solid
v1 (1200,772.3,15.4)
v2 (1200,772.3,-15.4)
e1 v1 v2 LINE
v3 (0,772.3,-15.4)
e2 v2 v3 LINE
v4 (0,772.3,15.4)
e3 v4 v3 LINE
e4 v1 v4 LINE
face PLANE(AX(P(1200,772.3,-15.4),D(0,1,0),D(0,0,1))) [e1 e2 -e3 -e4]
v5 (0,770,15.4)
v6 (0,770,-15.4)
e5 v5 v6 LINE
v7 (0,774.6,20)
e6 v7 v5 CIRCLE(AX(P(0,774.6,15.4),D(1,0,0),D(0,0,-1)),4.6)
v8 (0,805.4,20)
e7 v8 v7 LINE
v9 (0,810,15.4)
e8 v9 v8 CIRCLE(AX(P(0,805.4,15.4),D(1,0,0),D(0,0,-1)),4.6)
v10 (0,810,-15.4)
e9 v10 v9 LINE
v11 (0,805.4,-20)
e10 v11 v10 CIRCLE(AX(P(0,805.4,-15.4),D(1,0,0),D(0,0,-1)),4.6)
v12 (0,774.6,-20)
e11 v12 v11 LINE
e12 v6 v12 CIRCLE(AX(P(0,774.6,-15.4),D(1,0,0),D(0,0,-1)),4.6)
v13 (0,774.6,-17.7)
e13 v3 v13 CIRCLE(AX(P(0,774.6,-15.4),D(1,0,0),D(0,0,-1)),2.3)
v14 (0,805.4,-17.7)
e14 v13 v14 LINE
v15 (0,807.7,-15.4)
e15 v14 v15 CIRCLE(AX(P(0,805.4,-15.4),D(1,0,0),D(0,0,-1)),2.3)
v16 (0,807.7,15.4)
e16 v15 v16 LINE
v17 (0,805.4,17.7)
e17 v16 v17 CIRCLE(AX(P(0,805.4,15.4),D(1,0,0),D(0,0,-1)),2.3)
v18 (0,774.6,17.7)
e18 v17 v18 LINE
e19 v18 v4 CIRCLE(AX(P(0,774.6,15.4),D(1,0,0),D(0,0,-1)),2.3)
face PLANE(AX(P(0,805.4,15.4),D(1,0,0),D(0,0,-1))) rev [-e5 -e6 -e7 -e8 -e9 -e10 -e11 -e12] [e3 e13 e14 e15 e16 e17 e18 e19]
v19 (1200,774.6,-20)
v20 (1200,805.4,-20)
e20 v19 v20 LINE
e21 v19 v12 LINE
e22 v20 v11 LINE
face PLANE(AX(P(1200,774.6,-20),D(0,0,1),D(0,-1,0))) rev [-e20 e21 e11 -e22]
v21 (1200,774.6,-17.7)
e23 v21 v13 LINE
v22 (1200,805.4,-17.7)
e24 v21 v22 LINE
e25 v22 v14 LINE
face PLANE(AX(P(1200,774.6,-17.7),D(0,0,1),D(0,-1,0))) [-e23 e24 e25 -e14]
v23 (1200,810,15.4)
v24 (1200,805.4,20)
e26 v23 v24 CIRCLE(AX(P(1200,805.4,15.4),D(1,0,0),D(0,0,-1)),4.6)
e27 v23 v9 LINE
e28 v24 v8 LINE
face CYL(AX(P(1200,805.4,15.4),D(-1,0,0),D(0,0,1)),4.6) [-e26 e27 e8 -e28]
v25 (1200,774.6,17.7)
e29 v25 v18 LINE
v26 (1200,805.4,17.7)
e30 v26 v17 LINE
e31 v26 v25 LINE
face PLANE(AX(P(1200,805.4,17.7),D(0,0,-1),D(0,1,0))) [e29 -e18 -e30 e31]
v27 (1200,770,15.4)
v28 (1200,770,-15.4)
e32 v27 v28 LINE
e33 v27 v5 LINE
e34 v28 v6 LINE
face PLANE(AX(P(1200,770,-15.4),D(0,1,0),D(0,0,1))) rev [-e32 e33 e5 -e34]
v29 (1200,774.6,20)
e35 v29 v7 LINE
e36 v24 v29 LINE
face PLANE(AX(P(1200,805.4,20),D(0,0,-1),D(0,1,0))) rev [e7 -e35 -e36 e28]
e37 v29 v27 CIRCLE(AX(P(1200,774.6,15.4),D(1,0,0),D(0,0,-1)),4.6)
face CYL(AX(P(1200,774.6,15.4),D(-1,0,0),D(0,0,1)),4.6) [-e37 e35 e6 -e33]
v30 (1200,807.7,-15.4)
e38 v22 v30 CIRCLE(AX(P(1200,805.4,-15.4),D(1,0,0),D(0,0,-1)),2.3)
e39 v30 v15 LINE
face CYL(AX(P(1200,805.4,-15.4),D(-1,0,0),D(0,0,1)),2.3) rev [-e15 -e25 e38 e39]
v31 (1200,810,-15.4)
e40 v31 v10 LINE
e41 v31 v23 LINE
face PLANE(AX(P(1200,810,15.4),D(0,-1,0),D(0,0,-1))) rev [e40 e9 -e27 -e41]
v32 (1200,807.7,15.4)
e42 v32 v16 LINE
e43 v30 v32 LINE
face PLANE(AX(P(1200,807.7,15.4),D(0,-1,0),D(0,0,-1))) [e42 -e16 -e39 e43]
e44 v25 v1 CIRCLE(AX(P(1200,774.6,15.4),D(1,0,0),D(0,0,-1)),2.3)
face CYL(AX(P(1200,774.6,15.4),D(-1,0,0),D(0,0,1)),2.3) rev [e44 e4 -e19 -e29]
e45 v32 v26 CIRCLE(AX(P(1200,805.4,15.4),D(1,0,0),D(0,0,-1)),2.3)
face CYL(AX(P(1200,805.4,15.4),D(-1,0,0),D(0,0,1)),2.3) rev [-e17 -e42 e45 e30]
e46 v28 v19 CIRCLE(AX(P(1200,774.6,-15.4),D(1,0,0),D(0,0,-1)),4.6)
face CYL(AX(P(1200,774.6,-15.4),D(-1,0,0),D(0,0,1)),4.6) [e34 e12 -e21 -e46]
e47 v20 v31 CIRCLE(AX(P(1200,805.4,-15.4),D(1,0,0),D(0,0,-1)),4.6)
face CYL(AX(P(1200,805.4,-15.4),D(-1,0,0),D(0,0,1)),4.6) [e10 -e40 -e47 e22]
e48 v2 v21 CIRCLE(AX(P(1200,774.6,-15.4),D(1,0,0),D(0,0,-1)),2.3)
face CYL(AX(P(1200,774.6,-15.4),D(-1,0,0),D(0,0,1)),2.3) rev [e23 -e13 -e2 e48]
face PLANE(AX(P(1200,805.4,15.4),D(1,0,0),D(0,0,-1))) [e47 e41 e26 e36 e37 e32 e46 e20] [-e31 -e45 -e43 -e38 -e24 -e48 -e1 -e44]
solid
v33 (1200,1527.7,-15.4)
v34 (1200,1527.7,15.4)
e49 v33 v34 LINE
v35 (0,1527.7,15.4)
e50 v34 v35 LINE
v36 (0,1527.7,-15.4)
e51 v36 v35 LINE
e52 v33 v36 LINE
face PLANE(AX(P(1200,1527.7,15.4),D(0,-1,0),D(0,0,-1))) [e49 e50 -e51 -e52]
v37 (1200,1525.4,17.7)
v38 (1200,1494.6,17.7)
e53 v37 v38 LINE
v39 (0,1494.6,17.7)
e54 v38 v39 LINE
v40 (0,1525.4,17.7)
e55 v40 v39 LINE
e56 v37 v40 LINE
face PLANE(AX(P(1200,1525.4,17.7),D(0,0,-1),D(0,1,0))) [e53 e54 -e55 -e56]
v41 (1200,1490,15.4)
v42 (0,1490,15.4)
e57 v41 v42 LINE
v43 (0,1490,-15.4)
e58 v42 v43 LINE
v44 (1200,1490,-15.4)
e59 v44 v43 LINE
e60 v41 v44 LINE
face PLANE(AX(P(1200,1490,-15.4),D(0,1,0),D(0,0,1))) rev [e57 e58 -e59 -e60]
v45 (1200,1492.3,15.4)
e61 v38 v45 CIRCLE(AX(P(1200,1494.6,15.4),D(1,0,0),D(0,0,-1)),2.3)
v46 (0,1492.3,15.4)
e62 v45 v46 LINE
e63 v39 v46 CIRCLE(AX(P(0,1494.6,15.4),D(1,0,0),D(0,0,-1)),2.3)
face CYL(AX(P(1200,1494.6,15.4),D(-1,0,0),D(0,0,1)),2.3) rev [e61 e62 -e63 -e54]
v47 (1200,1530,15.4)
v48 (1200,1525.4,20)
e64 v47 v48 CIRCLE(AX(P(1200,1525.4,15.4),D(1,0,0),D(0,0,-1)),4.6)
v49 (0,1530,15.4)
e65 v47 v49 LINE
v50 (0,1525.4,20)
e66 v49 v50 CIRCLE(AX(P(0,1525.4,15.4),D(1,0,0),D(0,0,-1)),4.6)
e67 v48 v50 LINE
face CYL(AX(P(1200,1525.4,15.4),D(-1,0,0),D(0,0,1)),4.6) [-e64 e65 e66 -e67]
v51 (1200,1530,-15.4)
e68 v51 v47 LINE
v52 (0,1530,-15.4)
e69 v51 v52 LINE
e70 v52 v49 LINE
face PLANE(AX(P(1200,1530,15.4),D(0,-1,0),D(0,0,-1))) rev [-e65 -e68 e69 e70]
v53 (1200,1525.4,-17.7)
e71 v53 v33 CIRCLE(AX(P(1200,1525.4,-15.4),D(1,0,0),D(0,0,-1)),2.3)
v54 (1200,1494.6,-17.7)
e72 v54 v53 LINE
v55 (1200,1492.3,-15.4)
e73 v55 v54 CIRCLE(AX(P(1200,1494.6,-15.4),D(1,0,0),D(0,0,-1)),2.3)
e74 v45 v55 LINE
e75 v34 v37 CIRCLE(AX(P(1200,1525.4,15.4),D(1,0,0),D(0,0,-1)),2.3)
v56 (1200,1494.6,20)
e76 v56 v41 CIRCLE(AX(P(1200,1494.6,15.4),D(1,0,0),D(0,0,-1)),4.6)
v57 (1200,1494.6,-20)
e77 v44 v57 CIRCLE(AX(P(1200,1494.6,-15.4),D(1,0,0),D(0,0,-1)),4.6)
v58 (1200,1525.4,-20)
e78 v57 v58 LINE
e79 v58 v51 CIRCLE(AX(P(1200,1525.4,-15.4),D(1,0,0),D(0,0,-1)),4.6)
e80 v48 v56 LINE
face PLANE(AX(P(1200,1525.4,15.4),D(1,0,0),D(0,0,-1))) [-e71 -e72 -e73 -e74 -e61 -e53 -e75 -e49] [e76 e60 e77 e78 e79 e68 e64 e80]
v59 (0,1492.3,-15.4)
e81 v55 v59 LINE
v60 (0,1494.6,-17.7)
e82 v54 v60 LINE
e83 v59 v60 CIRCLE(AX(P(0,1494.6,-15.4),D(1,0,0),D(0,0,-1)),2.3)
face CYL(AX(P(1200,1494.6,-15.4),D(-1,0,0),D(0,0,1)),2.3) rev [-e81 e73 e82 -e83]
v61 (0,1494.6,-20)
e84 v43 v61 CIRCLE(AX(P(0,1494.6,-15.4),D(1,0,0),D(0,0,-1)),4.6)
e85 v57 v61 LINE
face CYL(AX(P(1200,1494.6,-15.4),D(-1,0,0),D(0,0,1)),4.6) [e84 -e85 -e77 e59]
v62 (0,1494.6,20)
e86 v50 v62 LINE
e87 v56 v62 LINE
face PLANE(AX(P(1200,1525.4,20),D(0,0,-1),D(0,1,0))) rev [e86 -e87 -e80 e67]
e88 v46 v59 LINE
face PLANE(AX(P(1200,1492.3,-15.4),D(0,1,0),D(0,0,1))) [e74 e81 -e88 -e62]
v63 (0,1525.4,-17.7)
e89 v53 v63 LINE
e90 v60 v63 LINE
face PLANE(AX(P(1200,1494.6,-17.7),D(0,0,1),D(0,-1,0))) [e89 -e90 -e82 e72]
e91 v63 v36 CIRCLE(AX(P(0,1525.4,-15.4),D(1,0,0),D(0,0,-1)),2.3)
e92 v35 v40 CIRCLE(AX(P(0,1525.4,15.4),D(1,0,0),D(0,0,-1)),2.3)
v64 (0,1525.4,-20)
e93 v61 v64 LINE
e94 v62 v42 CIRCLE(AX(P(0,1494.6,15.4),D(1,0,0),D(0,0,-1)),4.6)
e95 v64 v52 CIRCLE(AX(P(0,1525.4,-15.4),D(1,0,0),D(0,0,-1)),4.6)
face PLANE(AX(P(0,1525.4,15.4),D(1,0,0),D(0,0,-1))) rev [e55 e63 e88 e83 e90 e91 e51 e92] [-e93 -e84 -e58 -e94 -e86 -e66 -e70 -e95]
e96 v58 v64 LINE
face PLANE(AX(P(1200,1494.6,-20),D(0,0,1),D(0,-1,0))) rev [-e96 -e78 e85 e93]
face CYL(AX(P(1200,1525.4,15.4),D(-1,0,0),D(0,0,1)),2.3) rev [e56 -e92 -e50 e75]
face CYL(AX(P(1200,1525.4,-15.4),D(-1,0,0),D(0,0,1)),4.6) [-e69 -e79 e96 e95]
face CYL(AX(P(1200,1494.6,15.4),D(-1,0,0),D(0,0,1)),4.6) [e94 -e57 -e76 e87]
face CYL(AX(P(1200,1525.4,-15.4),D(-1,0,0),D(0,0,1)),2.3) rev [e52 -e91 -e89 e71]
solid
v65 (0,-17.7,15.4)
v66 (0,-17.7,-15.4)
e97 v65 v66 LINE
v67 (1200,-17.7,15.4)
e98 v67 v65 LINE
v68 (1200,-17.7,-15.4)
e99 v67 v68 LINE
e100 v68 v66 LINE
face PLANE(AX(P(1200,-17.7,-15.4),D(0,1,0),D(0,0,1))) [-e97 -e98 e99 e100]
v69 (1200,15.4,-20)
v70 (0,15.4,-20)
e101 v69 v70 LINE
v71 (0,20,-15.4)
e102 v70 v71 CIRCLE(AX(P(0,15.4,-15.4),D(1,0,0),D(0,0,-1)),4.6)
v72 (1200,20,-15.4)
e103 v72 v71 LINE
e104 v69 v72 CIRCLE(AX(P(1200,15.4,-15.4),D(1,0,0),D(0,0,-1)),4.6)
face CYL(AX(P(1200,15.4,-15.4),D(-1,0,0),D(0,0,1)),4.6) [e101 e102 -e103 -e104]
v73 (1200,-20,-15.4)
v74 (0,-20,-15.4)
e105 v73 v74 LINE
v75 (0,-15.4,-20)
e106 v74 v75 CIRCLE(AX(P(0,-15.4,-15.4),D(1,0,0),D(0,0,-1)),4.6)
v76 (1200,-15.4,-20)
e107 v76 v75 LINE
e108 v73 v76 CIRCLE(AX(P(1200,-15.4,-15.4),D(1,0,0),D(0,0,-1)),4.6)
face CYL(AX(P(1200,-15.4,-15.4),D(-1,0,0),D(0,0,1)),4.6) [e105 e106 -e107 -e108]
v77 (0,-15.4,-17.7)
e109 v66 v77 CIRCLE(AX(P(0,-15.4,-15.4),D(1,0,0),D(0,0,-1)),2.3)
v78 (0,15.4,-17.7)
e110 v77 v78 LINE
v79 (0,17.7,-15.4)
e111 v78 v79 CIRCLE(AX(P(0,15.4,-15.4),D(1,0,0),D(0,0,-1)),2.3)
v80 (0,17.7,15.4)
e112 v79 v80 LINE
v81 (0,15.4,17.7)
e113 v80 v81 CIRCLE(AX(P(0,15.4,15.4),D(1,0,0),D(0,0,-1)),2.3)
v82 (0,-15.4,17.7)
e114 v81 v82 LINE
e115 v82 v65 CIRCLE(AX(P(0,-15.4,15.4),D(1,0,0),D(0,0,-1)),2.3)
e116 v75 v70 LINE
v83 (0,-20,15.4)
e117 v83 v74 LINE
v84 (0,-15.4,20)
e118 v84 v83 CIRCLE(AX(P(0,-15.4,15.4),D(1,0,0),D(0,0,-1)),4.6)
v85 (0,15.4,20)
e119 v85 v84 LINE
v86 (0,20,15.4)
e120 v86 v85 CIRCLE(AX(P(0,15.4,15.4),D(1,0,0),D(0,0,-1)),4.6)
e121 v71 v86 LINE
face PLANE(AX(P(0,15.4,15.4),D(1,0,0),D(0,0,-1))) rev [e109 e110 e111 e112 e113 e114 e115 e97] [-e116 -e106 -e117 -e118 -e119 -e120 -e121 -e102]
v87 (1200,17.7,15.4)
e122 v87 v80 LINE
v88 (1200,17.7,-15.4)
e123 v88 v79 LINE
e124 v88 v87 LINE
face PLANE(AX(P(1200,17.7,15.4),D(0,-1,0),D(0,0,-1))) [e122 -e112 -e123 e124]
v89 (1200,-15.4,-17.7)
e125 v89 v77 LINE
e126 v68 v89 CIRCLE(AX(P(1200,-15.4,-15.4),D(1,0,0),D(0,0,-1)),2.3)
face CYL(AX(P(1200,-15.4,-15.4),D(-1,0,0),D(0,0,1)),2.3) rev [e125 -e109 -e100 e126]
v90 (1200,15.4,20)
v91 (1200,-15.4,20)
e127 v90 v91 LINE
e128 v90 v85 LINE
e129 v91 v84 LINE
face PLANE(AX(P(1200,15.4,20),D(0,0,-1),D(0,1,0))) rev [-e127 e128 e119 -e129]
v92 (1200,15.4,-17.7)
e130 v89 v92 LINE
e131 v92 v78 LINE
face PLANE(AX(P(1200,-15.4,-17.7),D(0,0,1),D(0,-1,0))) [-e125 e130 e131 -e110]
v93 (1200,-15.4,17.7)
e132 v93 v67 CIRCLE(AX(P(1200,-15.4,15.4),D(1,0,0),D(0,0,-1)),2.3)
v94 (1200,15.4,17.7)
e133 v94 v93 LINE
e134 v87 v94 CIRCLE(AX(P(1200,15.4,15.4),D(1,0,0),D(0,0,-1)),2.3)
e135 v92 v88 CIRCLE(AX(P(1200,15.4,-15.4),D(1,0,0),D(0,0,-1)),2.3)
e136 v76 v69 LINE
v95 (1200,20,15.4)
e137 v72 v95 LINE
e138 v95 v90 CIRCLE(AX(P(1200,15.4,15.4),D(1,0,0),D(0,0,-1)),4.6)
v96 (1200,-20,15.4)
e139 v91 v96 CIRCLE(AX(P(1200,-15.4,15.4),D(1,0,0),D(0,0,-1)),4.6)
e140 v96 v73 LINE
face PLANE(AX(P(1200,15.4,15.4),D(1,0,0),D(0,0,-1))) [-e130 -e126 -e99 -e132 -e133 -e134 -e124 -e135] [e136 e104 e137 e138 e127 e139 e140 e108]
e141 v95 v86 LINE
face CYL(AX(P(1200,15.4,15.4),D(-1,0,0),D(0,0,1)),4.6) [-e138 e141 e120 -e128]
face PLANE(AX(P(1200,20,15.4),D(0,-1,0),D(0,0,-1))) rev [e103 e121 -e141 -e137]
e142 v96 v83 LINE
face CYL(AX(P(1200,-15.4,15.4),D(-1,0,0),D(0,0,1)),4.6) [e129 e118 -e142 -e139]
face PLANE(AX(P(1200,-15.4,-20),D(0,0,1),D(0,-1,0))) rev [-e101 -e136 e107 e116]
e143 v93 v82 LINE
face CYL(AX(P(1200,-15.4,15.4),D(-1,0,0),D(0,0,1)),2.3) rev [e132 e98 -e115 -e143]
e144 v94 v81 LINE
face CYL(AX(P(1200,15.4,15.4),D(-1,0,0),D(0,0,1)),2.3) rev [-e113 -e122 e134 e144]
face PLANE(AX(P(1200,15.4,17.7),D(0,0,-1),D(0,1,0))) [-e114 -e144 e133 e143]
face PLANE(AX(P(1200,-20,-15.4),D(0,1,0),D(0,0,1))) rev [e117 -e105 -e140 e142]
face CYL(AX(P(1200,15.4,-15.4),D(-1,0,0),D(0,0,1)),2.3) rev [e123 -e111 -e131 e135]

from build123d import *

# Parameters (mm, degrees)
SQUARE_TUBE_40_X_40_X_2_3_1_DEPTH   = 1200
SQUARE_TUBE_40_X_40_X_2_3_1_2_DEPTH = 1200
SQUARE_TUBE_40_X_40_X_2_3_1_3_DEPTH = 1200


with BuildPart() as part:
    # Sketch11 → Square Tube 40 X 40 X 2.3(1) (new body)
    with BuildSketch(Plane.YZ):
        with BuildLine():
            Line((-15.4, -20), (15.4, -20))
            ThreePointArc((15.4, -20), (18.652691193, -18.652691193), (20, -15.4))
            Line((20, -15.4), (20, 15.4))
            ThreePointArc((20, 15.4), (18.652691193, 18.652691193), (15.4, 20))
            Line((15.4, 20), (-15.4, 20))
            ThreePointArc((-15.4, 20), (-18.652691193, 18.652691193), (-20, 15.4))
            Line((-20, 15.4), (-20, -15.4))
            ThreePointArc((-20, -15.4), (-18.652691193, -18.652691193), (-15.4, -20))
        make_face()
        with BuildLine():
            Line((-15.4, -17.7), (15.4, -17.7))
            ThreePointArc((15.4, -17.7), (17.026345597, -17.026345597), (17.7, -15.4))
            Line((17.7, -15.4), (17.7, 15.4))
            ThreePointArc((17.7, 15.4), (17.026345597, 17.026345597), (15.4, 17.7))
            Line((15.4, 17.7), (-15.4, 17.7))
            ThreePointArc((-15.4, 17.7), (-17.026345597, 17.026345597), (-17.7, 15.4))
            Line((-17.7, 15.4), (-17.7, -15.4))
            ThreePointArc((-17.7, -15.4), (-17.026345597, -17.026345597), (-15.4, -17.7))
        make_face(mode=Mode.SUBTRACT)
    extrude(amount=SQUARE_TUBE_40_X_40_X_2_3_1_DEPTH)


with BuildPart() as body_2:
    # Sketch11 on segment 2 (carried to segment 2) → Square Tube 40 X 40 X 2.3_1 2 (new body)
    with BuildSketch(Plane(origin=(0, 1510, 0), x_dir=(0, 1, 0), z_dir=(1, 0, 0))):
        with BuildLine():
            Line((-15.4, -20), (15.4, -20))
            ThreePointArc((15.4, -20), (18.652691193, -18.652691193), (20, -15.4))
            Line((20, -15.4), (20, 15.4))
            ThreePointArc((20, 15.4), (18.652691193, 18.652691193), (15.4, 20))
            Line((15.4, 20), (-15.4, 20))
            ThreePointArc((-15.4, 20), (-18.652691193, 18.652691193), (-20, 15.4))
            Line((-20, 15.4), (-20, -15.4))
            ThreePointArc((-20, -15.4), (-18.652691193, -18.652691193), (-15.4, -20))
        make_face()
        with BuildLine():
            Line((-15.4, -17.7), (15.4, -17.7))
            ThreePointArc((15.4, -17.7), (17.026345597, -17.026345597), (17.7, -15.4))
            Line((17.7, -15.4), (17.7, 15.4))
            ThreePointArc((17.7, 15.4), (17.026345597, 17.026345597), (15.4, 17.7))
            Line((15.4, 17.7), (-15.4, 17.7))
            ThreePointArc((-15.4, 17.7), (-17.026345597, 17.026345597), (-17.7, 15.4))
            Line((-17.7, 15.4), (-17.7, -15.4))
            ThreePointArc((-17.7, -15.4), (-17.026345597, -17.026345597), (-15.4, -17.7))
        make_face(mode=Mode.SUBTRACT)
    extrude(amount=SQUARE_TUBE_40_X_40_X_2_3_1_2_DEPTH)


with BuildPart() as body_3:
    # Sketch11 on segment 3 (carried to segment 3) → Square Tube 40 X 40 X 2.3_1 3 (new body)
    with BuildSketch(Plane(origin=(0, 790, 0), x_dir=(0, 1, 0), z_dir=(1, 0, 0))):
        with BuildLine():
            Line((-15.4, -20), (15.4, -20))
            ThreePointArc((15.4, -20), (18.652691193, -18.652691193), (20, -15.4))
            Line((20, -15.4), (20, 15.4))
            ThreePointArc((20, 15.4), (18.652691193, 18.652691193), (15.4, 20))
            Line((15.4, 20), (-15.4, 20))
            ThreePointArc((-15.4, 20), (-18.652691193, 18.652691193), (-20, 15.4))
            Line((-20, 15.4), (-20, -15.4))
            ThreePointArc((-20, -15.4), (-18.652691193, -18.652691193), (-15.4, -20))
        make_face()
        with BuildLine():
            Line((-15.4, -17.7), (15.4, -17.7))
            ThreePointArc((15.4, -17.7), (17.026345597, -17.026345597), (17.7, -15.4))
            Line((17.7, -15.4), (17.7, 15.4))
            ThreePointArc((17.7, 15.4), (17.026345597, 17.026345597), (15.4, 17.7))
            Line((15.4, 17.7), (-15.4, 17.7))
            ThreePointArc((-15.4, 17.7), (-17.026345597, 17.026345597), (-17.7, 15.4))
            Line((-17.7, 15.4), (-17.7, -15.4))
            ThreePointArc((-17.7, -15.4), (-17.026345597, -17.026345597), (-15.4, -17.7))
        make_face(mode=Mode.SUBTRACT)
    extrude(amount=SQUARE_TUBE_40_X_40_X_2_3_1_3_DEPTH)


solid = Compound([part.part, body_2.part, body_3.part])
